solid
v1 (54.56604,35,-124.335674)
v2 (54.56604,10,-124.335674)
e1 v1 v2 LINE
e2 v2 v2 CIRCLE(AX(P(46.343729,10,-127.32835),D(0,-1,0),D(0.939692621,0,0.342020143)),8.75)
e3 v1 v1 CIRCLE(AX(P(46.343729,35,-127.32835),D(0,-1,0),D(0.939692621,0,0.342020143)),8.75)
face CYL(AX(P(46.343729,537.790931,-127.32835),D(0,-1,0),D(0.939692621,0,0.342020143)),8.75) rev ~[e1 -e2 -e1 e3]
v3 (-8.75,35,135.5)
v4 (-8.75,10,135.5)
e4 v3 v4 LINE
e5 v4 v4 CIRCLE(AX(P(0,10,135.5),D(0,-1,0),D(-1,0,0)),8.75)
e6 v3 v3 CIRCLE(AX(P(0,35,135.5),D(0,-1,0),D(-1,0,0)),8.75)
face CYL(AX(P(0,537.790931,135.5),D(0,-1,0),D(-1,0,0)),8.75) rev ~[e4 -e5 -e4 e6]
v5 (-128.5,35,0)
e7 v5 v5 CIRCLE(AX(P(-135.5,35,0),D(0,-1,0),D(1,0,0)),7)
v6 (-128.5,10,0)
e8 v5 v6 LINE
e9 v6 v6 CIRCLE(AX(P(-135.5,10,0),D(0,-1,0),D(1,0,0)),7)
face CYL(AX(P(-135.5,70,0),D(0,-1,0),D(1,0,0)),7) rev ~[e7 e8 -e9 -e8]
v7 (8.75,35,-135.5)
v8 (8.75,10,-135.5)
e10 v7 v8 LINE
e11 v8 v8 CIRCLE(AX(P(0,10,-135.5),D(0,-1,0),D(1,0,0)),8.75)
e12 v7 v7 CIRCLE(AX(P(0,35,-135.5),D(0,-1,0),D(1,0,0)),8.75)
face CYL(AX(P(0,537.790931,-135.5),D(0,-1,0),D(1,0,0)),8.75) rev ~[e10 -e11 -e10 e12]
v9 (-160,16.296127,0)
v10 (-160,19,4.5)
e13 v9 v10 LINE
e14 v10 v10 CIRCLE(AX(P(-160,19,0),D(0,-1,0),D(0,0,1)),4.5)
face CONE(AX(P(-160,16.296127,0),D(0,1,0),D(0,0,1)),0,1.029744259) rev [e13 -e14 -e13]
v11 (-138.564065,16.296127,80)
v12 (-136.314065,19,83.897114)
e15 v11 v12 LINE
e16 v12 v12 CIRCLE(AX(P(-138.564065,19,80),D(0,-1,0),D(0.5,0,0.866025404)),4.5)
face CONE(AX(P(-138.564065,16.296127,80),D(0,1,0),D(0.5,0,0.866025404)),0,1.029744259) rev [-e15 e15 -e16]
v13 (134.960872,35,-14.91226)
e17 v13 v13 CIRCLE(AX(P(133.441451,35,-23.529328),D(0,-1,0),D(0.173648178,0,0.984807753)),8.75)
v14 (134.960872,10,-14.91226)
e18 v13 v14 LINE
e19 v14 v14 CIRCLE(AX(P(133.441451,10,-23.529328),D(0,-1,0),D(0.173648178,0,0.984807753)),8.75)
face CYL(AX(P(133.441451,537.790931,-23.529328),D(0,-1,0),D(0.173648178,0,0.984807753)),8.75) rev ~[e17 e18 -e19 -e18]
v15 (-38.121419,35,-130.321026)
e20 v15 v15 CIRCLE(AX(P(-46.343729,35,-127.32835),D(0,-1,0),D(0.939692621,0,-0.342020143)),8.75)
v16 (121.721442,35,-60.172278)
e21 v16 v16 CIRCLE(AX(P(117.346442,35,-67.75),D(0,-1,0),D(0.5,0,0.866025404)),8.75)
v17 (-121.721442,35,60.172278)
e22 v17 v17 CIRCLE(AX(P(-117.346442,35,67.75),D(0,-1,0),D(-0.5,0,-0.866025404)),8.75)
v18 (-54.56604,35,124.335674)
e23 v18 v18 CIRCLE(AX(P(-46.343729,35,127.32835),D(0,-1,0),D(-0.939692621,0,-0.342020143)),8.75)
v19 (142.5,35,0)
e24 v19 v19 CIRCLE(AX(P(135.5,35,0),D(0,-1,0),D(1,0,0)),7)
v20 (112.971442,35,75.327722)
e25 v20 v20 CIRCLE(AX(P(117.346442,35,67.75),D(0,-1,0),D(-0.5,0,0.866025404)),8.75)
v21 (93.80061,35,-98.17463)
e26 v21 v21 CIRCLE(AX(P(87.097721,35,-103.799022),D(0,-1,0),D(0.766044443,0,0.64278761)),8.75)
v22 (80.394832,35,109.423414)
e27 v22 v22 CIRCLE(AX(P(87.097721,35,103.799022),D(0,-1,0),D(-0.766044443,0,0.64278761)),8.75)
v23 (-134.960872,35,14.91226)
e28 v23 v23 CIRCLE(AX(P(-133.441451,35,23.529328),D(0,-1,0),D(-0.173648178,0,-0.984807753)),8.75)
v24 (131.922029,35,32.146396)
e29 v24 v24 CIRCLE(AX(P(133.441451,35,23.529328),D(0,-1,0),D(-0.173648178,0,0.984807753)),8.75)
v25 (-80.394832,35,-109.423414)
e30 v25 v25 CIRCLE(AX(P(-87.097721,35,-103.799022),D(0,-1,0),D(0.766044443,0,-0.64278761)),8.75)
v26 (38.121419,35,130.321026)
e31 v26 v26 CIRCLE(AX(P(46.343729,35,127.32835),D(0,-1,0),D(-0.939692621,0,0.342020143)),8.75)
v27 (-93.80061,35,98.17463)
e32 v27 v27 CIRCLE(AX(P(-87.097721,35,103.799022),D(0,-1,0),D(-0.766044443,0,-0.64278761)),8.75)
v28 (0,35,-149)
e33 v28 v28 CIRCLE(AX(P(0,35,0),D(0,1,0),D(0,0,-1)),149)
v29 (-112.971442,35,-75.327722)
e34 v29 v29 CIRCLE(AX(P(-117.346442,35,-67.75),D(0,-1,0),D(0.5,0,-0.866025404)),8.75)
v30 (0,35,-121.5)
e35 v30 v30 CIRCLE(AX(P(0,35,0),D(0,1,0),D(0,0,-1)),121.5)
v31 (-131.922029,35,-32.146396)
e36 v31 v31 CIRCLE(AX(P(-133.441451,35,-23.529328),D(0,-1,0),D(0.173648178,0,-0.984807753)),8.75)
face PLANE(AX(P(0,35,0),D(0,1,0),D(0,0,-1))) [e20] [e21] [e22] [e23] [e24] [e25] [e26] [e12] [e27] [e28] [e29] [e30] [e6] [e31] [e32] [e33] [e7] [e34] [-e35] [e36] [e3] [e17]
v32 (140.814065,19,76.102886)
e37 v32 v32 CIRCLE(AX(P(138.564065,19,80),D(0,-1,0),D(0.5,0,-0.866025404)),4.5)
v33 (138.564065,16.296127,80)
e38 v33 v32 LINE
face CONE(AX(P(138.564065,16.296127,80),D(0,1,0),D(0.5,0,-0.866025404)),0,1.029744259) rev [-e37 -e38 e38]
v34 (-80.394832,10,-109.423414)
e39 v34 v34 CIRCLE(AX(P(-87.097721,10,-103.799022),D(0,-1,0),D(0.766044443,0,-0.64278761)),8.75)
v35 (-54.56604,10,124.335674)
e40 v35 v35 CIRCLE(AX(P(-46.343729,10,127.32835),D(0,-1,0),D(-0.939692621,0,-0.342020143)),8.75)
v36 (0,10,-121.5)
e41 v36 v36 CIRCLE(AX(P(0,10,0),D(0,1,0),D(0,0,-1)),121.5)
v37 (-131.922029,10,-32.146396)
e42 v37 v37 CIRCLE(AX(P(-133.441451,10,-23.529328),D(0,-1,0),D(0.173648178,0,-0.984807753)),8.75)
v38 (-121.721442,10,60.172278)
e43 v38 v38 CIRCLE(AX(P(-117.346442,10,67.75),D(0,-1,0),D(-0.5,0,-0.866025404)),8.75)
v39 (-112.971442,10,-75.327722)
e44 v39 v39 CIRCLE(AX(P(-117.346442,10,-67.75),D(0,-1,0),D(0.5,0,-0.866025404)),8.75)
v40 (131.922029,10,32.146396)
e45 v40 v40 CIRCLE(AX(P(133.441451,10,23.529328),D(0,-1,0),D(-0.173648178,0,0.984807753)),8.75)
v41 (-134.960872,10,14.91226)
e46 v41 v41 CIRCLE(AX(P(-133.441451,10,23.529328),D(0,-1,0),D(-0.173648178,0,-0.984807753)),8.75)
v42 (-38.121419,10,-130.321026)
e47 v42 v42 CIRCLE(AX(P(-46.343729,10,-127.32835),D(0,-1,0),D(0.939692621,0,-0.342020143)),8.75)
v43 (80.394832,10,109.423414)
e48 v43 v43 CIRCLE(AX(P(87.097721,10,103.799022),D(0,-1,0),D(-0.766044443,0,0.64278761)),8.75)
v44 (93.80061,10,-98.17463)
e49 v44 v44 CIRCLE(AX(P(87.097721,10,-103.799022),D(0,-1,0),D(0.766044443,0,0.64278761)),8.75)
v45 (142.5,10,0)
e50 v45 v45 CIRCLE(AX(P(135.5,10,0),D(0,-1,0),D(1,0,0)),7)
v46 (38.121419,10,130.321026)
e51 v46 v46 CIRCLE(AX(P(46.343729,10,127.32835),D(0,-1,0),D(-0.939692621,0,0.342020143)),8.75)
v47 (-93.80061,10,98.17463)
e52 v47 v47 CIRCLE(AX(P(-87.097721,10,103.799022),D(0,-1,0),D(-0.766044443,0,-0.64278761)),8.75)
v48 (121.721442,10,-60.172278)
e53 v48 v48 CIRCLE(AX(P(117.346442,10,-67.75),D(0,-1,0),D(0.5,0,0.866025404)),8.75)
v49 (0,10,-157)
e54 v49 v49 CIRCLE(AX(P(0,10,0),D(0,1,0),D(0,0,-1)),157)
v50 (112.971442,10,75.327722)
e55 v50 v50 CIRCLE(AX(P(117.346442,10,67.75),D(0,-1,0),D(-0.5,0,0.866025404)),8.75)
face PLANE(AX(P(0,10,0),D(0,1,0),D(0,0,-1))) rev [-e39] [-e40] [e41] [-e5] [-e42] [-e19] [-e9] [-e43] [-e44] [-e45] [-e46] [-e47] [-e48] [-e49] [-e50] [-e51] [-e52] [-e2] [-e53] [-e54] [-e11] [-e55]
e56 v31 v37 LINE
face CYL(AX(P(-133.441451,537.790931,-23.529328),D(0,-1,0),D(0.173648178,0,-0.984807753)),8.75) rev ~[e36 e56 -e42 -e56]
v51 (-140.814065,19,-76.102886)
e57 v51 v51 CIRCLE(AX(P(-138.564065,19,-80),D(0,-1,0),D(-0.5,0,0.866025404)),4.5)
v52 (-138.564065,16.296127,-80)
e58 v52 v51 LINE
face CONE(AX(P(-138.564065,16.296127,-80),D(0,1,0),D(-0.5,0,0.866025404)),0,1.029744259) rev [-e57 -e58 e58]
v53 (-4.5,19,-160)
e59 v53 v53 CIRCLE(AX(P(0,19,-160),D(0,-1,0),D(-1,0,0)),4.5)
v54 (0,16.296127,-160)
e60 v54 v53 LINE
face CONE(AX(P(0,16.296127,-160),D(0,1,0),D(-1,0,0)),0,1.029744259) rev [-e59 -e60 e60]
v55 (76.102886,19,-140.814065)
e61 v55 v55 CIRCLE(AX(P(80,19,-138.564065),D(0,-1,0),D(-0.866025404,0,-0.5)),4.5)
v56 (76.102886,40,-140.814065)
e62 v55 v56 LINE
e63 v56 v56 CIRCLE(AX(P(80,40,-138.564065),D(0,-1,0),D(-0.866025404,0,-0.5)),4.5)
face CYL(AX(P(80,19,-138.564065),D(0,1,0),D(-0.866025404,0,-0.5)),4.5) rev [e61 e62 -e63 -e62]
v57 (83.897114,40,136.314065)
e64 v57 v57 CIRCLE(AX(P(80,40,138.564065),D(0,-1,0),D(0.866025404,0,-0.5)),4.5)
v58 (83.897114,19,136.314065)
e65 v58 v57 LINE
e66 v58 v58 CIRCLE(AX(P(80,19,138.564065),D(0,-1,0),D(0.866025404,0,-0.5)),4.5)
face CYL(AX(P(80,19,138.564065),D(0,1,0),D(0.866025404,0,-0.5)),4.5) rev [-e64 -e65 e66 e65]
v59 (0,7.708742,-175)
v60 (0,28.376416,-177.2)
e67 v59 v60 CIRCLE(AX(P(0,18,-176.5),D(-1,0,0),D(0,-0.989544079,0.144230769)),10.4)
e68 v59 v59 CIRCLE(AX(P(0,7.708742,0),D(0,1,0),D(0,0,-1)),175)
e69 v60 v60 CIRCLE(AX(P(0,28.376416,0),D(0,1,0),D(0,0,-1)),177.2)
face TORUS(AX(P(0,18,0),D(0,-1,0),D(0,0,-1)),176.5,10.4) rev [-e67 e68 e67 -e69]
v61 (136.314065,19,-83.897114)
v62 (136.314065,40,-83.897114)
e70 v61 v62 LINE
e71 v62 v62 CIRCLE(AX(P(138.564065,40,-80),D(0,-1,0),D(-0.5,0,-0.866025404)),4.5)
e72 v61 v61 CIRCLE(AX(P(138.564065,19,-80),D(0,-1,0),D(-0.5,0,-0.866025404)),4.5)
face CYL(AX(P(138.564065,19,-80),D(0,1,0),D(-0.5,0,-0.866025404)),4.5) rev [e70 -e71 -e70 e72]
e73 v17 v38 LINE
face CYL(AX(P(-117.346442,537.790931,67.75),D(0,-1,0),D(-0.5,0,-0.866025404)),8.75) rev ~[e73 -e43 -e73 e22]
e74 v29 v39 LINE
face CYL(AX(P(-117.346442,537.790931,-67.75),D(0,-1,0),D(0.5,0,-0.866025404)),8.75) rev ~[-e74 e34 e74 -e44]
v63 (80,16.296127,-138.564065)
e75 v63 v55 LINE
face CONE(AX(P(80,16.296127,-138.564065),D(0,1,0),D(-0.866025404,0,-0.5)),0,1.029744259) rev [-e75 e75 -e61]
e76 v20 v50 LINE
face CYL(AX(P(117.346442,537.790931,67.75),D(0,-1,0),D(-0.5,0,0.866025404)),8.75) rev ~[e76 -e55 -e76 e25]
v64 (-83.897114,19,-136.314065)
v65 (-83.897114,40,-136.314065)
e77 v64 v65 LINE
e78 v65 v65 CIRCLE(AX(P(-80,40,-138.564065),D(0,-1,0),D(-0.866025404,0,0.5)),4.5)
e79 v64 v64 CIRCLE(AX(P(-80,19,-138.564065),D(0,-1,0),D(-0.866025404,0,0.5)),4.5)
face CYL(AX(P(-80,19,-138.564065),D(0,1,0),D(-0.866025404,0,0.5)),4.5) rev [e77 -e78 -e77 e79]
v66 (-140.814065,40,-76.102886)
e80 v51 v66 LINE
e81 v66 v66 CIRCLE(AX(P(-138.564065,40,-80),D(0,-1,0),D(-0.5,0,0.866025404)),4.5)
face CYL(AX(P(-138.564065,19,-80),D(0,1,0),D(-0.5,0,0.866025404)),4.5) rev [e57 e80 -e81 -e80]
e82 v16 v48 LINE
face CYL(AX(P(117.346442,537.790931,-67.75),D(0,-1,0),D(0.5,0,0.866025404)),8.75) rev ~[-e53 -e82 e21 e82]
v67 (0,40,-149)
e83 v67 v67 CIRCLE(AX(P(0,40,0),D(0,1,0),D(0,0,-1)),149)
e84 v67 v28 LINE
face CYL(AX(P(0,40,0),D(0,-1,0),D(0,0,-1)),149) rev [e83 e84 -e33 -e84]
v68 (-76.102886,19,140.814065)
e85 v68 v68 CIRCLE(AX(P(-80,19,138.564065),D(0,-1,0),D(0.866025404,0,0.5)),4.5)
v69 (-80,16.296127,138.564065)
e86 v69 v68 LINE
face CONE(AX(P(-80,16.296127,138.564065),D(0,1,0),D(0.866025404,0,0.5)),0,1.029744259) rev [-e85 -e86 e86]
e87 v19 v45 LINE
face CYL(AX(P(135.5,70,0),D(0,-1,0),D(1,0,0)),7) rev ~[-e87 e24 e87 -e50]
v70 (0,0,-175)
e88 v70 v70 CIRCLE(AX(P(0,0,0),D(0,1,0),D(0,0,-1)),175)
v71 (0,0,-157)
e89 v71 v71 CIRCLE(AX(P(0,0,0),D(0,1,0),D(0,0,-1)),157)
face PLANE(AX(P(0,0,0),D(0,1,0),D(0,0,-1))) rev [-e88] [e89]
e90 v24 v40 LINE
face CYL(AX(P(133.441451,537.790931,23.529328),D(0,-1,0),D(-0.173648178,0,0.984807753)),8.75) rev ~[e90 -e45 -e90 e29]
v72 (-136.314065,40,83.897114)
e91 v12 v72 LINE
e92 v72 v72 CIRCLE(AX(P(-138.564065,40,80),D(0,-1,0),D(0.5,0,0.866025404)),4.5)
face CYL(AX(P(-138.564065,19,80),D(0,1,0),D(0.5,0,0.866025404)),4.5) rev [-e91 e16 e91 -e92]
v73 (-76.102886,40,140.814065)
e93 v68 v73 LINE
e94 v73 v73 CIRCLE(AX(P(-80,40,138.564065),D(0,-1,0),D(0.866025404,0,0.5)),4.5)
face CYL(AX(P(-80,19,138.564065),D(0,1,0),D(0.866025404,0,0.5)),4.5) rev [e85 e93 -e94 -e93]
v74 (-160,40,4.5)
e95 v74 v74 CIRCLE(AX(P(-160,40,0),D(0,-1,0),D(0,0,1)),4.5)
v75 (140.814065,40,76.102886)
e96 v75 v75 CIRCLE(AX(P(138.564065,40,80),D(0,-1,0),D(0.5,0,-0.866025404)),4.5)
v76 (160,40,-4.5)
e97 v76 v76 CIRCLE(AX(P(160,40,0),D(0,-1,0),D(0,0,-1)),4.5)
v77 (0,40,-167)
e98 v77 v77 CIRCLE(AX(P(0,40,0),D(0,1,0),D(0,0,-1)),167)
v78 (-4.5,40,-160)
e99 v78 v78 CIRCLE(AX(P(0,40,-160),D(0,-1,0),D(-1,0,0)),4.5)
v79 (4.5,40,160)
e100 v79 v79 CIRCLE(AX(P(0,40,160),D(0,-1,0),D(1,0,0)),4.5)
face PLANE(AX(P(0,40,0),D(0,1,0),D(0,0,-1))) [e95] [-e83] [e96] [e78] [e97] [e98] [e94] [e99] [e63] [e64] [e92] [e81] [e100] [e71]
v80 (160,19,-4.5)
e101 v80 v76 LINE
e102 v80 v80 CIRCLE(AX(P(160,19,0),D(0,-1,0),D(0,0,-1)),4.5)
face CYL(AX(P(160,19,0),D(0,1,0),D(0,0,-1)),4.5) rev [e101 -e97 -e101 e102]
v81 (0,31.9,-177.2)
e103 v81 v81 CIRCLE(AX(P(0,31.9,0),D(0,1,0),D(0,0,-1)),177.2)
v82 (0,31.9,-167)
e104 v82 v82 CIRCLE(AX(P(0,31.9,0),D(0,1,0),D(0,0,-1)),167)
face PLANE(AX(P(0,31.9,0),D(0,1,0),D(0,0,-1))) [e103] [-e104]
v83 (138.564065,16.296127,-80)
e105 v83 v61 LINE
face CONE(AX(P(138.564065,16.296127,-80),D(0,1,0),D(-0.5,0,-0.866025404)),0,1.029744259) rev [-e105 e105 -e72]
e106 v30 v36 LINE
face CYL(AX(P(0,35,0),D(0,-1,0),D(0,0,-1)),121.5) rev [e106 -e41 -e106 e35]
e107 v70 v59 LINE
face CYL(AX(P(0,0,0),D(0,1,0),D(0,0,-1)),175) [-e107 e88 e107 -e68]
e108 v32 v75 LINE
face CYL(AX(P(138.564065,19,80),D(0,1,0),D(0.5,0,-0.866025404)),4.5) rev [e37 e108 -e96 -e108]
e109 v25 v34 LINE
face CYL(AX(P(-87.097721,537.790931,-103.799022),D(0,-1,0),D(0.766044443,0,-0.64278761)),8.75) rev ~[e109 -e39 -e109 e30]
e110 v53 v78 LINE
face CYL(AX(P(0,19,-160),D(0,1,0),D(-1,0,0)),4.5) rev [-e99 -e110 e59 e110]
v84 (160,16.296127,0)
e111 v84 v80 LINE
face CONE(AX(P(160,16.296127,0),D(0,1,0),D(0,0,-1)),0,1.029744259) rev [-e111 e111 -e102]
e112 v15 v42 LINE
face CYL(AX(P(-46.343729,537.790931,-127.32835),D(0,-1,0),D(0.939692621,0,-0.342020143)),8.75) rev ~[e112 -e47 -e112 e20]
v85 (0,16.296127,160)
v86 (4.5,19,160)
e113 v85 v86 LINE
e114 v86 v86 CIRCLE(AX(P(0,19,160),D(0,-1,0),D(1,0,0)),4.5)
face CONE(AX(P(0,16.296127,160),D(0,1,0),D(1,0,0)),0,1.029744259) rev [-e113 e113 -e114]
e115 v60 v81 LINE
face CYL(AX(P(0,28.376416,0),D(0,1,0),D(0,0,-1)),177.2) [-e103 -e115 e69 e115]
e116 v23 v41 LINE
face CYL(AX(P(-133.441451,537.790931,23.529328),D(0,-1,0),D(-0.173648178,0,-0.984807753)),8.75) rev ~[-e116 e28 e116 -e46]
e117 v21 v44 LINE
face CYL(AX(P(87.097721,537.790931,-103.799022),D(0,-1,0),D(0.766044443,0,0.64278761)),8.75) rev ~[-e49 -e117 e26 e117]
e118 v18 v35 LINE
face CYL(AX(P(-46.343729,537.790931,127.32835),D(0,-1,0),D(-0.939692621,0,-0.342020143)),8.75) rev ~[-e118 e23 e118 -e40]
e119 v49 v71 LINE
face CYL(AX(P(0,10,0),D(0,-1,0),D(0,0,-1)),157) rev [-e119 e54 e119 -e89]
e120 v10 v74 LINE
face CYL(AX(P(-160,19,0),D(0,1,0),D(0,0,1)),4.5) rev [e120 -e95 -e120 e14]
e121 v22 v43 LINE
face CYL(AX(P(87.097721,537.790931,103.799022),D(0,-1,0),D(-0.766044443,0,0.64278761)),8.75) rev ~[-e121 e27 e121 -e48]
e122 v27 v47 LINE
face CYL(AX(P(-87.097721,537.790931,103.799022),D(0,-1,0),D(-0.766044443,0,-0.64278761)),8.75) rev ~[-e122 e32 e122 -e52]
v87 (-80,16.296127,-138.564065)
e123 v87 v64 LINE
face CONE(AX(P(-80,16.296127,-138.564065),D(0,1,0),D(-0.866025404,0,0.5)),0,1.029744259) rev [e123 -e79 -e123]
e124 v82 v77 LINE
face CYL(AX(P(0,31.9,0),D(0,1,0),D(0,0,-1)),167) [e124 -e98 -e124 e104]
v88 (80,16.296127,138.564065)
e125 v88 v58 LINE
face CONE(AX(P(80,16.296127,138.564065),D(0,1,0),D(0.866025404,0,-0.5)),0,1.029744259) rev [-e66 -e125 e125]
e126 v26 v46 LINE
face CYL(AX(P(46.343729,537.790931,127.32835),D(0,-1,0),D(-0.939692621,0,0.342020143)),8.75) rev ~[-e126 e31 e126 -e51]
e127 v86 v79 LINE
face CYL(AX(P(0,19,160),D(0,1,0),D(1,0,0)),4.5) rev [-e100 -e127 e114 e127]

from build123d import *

# Parameters (mm, degrees)
CIRPATTERN1_COUNT            = 12
F_0_17_0_17_DIAMETER_HOLE1_D = 17.5
CIRPATTERN2_COUNT            = 18
M16_TAPPED_HOLE1_D           = 14
M16_TAPPED_HOLE1_DEPTH       = 35
M16_TAPPED_HOLE1_TIP         = 4.206024333


with BuildPart() as part:
    # Sketch1 → Revolve1 (revolve)
    with BuildSketch(Plane.XY, mode=Mode.PRIVATE) as revolve1_sk:
        with BuildLine():
            Line((-157, 0), (-175, 0))
            Line((-175, 0), (-175, 7.708741574))
            ThreePointArc((-175, 7.708741574), (-166.158424343, 19.100823753), (-177.2, 28.376415566))
            Line((-177.2, 28.376415566), (-177.2, 31.9))
            Line((-177.2, 31.9), (-167, 31.9))
            Line((-167, 31.9), (-167, 40))
            Line((-167, 40), (-149, 40))
            Line((-149, 40), (-149, 35))
            Line((-149, 35), (-121.5, 35))
            Line((-121.5, 35), (-121.5, 10))
            Line((-121.5, 10), (-157, 10))
            Line((-157, 10), (-157, 0))
        make_face()
    revolve(revolve1_sk.sketch.rotate(Axis((0, 22.704798349, 0), (0, 1, 0)), 270), axis=Axis((0, 22.704798349, 0), (0, 1, 0)))

    # Sketch2 → M10x1.0 Tapped Hole1 (revolve, cut)
    with BuildSketch(Plane(origin=(-160, 40, 0), x_dir=(0, 0, 1), z_dir=(1, 0, 0))):
        Polygon((0, 0), (0, 23.703872786), (4.5, 21), (4.5, 0), align=None)
    m10x1_0_tapped_hole1 = revolve(axis=Axis((-160, 46.35, 0), (0, -1, 0)), mode=Mode.SUBTRACT)

    # CirPattern1: M10x1.0 Tapped Hole1 ×12 about axis
    cirpattern1_axis = Axis((0, 0, 0), (0, 1, 0))
    for i in range(1, CIRPATTERN1_COUNT):
        add(m10x1_0_tapped_hole1.rotate(cirpattern1_axis, i * 360 / CIRPATTERN1_COUNT), mode=Mode.SUBTRACT)

    # Ø0.17 (0.17) Diameter Hole1 (through all)
    with Locations(Plane(origin=(0, 35, 0), x_dir=(-1, 0, 0), z_dir=(0, 1, 0))):
        with Locations((0, -135.5)):
            f_0_17_0_17_diameter_hole1 = Hole(F_0_17_0_17_DIAMETER_HOLE1_D / 2)

    # CirPattern2: Ø0.17 (0.17) Diameter Hole1 ×18 about axis
    cirpattern2_axis = Axis((0, 0, 0), (0, 1, 0))
    for i in range(1, CIRPATTERN2_COUNT):
        add(f_0_17_0_17_diameter_hole1.rotate(cirpattern2_axis, i * 360 / CIRPATTERN2_COUNT), mode=Mode.SUBTRACT)

    # M16 Tapped Hole1
    with Locations(Plane(origin=(0, 35, 0), x_dir=(-1, 0, 0), z_dir=(0, 1, 0))):
        with Locations((135.5, 0), (-135.5, 0)):
            Hole(M16_TAPPED_HOLE1_D / 2, depth=M16_TAPPED_HOLE1_DEPTH)
            with Locations((0, 0, -(M16_TAPPED_HOLE1_DEPTH + M16_TAPPED_HOLE1_TIP / 2))):  # 118° drill point
                Cone(0, M16_TAPPED_HOLE1_D / 2, M16_TAPPED_HOLE1_TIP, mode=Mode.SUBTRACT)


solid = part.part
